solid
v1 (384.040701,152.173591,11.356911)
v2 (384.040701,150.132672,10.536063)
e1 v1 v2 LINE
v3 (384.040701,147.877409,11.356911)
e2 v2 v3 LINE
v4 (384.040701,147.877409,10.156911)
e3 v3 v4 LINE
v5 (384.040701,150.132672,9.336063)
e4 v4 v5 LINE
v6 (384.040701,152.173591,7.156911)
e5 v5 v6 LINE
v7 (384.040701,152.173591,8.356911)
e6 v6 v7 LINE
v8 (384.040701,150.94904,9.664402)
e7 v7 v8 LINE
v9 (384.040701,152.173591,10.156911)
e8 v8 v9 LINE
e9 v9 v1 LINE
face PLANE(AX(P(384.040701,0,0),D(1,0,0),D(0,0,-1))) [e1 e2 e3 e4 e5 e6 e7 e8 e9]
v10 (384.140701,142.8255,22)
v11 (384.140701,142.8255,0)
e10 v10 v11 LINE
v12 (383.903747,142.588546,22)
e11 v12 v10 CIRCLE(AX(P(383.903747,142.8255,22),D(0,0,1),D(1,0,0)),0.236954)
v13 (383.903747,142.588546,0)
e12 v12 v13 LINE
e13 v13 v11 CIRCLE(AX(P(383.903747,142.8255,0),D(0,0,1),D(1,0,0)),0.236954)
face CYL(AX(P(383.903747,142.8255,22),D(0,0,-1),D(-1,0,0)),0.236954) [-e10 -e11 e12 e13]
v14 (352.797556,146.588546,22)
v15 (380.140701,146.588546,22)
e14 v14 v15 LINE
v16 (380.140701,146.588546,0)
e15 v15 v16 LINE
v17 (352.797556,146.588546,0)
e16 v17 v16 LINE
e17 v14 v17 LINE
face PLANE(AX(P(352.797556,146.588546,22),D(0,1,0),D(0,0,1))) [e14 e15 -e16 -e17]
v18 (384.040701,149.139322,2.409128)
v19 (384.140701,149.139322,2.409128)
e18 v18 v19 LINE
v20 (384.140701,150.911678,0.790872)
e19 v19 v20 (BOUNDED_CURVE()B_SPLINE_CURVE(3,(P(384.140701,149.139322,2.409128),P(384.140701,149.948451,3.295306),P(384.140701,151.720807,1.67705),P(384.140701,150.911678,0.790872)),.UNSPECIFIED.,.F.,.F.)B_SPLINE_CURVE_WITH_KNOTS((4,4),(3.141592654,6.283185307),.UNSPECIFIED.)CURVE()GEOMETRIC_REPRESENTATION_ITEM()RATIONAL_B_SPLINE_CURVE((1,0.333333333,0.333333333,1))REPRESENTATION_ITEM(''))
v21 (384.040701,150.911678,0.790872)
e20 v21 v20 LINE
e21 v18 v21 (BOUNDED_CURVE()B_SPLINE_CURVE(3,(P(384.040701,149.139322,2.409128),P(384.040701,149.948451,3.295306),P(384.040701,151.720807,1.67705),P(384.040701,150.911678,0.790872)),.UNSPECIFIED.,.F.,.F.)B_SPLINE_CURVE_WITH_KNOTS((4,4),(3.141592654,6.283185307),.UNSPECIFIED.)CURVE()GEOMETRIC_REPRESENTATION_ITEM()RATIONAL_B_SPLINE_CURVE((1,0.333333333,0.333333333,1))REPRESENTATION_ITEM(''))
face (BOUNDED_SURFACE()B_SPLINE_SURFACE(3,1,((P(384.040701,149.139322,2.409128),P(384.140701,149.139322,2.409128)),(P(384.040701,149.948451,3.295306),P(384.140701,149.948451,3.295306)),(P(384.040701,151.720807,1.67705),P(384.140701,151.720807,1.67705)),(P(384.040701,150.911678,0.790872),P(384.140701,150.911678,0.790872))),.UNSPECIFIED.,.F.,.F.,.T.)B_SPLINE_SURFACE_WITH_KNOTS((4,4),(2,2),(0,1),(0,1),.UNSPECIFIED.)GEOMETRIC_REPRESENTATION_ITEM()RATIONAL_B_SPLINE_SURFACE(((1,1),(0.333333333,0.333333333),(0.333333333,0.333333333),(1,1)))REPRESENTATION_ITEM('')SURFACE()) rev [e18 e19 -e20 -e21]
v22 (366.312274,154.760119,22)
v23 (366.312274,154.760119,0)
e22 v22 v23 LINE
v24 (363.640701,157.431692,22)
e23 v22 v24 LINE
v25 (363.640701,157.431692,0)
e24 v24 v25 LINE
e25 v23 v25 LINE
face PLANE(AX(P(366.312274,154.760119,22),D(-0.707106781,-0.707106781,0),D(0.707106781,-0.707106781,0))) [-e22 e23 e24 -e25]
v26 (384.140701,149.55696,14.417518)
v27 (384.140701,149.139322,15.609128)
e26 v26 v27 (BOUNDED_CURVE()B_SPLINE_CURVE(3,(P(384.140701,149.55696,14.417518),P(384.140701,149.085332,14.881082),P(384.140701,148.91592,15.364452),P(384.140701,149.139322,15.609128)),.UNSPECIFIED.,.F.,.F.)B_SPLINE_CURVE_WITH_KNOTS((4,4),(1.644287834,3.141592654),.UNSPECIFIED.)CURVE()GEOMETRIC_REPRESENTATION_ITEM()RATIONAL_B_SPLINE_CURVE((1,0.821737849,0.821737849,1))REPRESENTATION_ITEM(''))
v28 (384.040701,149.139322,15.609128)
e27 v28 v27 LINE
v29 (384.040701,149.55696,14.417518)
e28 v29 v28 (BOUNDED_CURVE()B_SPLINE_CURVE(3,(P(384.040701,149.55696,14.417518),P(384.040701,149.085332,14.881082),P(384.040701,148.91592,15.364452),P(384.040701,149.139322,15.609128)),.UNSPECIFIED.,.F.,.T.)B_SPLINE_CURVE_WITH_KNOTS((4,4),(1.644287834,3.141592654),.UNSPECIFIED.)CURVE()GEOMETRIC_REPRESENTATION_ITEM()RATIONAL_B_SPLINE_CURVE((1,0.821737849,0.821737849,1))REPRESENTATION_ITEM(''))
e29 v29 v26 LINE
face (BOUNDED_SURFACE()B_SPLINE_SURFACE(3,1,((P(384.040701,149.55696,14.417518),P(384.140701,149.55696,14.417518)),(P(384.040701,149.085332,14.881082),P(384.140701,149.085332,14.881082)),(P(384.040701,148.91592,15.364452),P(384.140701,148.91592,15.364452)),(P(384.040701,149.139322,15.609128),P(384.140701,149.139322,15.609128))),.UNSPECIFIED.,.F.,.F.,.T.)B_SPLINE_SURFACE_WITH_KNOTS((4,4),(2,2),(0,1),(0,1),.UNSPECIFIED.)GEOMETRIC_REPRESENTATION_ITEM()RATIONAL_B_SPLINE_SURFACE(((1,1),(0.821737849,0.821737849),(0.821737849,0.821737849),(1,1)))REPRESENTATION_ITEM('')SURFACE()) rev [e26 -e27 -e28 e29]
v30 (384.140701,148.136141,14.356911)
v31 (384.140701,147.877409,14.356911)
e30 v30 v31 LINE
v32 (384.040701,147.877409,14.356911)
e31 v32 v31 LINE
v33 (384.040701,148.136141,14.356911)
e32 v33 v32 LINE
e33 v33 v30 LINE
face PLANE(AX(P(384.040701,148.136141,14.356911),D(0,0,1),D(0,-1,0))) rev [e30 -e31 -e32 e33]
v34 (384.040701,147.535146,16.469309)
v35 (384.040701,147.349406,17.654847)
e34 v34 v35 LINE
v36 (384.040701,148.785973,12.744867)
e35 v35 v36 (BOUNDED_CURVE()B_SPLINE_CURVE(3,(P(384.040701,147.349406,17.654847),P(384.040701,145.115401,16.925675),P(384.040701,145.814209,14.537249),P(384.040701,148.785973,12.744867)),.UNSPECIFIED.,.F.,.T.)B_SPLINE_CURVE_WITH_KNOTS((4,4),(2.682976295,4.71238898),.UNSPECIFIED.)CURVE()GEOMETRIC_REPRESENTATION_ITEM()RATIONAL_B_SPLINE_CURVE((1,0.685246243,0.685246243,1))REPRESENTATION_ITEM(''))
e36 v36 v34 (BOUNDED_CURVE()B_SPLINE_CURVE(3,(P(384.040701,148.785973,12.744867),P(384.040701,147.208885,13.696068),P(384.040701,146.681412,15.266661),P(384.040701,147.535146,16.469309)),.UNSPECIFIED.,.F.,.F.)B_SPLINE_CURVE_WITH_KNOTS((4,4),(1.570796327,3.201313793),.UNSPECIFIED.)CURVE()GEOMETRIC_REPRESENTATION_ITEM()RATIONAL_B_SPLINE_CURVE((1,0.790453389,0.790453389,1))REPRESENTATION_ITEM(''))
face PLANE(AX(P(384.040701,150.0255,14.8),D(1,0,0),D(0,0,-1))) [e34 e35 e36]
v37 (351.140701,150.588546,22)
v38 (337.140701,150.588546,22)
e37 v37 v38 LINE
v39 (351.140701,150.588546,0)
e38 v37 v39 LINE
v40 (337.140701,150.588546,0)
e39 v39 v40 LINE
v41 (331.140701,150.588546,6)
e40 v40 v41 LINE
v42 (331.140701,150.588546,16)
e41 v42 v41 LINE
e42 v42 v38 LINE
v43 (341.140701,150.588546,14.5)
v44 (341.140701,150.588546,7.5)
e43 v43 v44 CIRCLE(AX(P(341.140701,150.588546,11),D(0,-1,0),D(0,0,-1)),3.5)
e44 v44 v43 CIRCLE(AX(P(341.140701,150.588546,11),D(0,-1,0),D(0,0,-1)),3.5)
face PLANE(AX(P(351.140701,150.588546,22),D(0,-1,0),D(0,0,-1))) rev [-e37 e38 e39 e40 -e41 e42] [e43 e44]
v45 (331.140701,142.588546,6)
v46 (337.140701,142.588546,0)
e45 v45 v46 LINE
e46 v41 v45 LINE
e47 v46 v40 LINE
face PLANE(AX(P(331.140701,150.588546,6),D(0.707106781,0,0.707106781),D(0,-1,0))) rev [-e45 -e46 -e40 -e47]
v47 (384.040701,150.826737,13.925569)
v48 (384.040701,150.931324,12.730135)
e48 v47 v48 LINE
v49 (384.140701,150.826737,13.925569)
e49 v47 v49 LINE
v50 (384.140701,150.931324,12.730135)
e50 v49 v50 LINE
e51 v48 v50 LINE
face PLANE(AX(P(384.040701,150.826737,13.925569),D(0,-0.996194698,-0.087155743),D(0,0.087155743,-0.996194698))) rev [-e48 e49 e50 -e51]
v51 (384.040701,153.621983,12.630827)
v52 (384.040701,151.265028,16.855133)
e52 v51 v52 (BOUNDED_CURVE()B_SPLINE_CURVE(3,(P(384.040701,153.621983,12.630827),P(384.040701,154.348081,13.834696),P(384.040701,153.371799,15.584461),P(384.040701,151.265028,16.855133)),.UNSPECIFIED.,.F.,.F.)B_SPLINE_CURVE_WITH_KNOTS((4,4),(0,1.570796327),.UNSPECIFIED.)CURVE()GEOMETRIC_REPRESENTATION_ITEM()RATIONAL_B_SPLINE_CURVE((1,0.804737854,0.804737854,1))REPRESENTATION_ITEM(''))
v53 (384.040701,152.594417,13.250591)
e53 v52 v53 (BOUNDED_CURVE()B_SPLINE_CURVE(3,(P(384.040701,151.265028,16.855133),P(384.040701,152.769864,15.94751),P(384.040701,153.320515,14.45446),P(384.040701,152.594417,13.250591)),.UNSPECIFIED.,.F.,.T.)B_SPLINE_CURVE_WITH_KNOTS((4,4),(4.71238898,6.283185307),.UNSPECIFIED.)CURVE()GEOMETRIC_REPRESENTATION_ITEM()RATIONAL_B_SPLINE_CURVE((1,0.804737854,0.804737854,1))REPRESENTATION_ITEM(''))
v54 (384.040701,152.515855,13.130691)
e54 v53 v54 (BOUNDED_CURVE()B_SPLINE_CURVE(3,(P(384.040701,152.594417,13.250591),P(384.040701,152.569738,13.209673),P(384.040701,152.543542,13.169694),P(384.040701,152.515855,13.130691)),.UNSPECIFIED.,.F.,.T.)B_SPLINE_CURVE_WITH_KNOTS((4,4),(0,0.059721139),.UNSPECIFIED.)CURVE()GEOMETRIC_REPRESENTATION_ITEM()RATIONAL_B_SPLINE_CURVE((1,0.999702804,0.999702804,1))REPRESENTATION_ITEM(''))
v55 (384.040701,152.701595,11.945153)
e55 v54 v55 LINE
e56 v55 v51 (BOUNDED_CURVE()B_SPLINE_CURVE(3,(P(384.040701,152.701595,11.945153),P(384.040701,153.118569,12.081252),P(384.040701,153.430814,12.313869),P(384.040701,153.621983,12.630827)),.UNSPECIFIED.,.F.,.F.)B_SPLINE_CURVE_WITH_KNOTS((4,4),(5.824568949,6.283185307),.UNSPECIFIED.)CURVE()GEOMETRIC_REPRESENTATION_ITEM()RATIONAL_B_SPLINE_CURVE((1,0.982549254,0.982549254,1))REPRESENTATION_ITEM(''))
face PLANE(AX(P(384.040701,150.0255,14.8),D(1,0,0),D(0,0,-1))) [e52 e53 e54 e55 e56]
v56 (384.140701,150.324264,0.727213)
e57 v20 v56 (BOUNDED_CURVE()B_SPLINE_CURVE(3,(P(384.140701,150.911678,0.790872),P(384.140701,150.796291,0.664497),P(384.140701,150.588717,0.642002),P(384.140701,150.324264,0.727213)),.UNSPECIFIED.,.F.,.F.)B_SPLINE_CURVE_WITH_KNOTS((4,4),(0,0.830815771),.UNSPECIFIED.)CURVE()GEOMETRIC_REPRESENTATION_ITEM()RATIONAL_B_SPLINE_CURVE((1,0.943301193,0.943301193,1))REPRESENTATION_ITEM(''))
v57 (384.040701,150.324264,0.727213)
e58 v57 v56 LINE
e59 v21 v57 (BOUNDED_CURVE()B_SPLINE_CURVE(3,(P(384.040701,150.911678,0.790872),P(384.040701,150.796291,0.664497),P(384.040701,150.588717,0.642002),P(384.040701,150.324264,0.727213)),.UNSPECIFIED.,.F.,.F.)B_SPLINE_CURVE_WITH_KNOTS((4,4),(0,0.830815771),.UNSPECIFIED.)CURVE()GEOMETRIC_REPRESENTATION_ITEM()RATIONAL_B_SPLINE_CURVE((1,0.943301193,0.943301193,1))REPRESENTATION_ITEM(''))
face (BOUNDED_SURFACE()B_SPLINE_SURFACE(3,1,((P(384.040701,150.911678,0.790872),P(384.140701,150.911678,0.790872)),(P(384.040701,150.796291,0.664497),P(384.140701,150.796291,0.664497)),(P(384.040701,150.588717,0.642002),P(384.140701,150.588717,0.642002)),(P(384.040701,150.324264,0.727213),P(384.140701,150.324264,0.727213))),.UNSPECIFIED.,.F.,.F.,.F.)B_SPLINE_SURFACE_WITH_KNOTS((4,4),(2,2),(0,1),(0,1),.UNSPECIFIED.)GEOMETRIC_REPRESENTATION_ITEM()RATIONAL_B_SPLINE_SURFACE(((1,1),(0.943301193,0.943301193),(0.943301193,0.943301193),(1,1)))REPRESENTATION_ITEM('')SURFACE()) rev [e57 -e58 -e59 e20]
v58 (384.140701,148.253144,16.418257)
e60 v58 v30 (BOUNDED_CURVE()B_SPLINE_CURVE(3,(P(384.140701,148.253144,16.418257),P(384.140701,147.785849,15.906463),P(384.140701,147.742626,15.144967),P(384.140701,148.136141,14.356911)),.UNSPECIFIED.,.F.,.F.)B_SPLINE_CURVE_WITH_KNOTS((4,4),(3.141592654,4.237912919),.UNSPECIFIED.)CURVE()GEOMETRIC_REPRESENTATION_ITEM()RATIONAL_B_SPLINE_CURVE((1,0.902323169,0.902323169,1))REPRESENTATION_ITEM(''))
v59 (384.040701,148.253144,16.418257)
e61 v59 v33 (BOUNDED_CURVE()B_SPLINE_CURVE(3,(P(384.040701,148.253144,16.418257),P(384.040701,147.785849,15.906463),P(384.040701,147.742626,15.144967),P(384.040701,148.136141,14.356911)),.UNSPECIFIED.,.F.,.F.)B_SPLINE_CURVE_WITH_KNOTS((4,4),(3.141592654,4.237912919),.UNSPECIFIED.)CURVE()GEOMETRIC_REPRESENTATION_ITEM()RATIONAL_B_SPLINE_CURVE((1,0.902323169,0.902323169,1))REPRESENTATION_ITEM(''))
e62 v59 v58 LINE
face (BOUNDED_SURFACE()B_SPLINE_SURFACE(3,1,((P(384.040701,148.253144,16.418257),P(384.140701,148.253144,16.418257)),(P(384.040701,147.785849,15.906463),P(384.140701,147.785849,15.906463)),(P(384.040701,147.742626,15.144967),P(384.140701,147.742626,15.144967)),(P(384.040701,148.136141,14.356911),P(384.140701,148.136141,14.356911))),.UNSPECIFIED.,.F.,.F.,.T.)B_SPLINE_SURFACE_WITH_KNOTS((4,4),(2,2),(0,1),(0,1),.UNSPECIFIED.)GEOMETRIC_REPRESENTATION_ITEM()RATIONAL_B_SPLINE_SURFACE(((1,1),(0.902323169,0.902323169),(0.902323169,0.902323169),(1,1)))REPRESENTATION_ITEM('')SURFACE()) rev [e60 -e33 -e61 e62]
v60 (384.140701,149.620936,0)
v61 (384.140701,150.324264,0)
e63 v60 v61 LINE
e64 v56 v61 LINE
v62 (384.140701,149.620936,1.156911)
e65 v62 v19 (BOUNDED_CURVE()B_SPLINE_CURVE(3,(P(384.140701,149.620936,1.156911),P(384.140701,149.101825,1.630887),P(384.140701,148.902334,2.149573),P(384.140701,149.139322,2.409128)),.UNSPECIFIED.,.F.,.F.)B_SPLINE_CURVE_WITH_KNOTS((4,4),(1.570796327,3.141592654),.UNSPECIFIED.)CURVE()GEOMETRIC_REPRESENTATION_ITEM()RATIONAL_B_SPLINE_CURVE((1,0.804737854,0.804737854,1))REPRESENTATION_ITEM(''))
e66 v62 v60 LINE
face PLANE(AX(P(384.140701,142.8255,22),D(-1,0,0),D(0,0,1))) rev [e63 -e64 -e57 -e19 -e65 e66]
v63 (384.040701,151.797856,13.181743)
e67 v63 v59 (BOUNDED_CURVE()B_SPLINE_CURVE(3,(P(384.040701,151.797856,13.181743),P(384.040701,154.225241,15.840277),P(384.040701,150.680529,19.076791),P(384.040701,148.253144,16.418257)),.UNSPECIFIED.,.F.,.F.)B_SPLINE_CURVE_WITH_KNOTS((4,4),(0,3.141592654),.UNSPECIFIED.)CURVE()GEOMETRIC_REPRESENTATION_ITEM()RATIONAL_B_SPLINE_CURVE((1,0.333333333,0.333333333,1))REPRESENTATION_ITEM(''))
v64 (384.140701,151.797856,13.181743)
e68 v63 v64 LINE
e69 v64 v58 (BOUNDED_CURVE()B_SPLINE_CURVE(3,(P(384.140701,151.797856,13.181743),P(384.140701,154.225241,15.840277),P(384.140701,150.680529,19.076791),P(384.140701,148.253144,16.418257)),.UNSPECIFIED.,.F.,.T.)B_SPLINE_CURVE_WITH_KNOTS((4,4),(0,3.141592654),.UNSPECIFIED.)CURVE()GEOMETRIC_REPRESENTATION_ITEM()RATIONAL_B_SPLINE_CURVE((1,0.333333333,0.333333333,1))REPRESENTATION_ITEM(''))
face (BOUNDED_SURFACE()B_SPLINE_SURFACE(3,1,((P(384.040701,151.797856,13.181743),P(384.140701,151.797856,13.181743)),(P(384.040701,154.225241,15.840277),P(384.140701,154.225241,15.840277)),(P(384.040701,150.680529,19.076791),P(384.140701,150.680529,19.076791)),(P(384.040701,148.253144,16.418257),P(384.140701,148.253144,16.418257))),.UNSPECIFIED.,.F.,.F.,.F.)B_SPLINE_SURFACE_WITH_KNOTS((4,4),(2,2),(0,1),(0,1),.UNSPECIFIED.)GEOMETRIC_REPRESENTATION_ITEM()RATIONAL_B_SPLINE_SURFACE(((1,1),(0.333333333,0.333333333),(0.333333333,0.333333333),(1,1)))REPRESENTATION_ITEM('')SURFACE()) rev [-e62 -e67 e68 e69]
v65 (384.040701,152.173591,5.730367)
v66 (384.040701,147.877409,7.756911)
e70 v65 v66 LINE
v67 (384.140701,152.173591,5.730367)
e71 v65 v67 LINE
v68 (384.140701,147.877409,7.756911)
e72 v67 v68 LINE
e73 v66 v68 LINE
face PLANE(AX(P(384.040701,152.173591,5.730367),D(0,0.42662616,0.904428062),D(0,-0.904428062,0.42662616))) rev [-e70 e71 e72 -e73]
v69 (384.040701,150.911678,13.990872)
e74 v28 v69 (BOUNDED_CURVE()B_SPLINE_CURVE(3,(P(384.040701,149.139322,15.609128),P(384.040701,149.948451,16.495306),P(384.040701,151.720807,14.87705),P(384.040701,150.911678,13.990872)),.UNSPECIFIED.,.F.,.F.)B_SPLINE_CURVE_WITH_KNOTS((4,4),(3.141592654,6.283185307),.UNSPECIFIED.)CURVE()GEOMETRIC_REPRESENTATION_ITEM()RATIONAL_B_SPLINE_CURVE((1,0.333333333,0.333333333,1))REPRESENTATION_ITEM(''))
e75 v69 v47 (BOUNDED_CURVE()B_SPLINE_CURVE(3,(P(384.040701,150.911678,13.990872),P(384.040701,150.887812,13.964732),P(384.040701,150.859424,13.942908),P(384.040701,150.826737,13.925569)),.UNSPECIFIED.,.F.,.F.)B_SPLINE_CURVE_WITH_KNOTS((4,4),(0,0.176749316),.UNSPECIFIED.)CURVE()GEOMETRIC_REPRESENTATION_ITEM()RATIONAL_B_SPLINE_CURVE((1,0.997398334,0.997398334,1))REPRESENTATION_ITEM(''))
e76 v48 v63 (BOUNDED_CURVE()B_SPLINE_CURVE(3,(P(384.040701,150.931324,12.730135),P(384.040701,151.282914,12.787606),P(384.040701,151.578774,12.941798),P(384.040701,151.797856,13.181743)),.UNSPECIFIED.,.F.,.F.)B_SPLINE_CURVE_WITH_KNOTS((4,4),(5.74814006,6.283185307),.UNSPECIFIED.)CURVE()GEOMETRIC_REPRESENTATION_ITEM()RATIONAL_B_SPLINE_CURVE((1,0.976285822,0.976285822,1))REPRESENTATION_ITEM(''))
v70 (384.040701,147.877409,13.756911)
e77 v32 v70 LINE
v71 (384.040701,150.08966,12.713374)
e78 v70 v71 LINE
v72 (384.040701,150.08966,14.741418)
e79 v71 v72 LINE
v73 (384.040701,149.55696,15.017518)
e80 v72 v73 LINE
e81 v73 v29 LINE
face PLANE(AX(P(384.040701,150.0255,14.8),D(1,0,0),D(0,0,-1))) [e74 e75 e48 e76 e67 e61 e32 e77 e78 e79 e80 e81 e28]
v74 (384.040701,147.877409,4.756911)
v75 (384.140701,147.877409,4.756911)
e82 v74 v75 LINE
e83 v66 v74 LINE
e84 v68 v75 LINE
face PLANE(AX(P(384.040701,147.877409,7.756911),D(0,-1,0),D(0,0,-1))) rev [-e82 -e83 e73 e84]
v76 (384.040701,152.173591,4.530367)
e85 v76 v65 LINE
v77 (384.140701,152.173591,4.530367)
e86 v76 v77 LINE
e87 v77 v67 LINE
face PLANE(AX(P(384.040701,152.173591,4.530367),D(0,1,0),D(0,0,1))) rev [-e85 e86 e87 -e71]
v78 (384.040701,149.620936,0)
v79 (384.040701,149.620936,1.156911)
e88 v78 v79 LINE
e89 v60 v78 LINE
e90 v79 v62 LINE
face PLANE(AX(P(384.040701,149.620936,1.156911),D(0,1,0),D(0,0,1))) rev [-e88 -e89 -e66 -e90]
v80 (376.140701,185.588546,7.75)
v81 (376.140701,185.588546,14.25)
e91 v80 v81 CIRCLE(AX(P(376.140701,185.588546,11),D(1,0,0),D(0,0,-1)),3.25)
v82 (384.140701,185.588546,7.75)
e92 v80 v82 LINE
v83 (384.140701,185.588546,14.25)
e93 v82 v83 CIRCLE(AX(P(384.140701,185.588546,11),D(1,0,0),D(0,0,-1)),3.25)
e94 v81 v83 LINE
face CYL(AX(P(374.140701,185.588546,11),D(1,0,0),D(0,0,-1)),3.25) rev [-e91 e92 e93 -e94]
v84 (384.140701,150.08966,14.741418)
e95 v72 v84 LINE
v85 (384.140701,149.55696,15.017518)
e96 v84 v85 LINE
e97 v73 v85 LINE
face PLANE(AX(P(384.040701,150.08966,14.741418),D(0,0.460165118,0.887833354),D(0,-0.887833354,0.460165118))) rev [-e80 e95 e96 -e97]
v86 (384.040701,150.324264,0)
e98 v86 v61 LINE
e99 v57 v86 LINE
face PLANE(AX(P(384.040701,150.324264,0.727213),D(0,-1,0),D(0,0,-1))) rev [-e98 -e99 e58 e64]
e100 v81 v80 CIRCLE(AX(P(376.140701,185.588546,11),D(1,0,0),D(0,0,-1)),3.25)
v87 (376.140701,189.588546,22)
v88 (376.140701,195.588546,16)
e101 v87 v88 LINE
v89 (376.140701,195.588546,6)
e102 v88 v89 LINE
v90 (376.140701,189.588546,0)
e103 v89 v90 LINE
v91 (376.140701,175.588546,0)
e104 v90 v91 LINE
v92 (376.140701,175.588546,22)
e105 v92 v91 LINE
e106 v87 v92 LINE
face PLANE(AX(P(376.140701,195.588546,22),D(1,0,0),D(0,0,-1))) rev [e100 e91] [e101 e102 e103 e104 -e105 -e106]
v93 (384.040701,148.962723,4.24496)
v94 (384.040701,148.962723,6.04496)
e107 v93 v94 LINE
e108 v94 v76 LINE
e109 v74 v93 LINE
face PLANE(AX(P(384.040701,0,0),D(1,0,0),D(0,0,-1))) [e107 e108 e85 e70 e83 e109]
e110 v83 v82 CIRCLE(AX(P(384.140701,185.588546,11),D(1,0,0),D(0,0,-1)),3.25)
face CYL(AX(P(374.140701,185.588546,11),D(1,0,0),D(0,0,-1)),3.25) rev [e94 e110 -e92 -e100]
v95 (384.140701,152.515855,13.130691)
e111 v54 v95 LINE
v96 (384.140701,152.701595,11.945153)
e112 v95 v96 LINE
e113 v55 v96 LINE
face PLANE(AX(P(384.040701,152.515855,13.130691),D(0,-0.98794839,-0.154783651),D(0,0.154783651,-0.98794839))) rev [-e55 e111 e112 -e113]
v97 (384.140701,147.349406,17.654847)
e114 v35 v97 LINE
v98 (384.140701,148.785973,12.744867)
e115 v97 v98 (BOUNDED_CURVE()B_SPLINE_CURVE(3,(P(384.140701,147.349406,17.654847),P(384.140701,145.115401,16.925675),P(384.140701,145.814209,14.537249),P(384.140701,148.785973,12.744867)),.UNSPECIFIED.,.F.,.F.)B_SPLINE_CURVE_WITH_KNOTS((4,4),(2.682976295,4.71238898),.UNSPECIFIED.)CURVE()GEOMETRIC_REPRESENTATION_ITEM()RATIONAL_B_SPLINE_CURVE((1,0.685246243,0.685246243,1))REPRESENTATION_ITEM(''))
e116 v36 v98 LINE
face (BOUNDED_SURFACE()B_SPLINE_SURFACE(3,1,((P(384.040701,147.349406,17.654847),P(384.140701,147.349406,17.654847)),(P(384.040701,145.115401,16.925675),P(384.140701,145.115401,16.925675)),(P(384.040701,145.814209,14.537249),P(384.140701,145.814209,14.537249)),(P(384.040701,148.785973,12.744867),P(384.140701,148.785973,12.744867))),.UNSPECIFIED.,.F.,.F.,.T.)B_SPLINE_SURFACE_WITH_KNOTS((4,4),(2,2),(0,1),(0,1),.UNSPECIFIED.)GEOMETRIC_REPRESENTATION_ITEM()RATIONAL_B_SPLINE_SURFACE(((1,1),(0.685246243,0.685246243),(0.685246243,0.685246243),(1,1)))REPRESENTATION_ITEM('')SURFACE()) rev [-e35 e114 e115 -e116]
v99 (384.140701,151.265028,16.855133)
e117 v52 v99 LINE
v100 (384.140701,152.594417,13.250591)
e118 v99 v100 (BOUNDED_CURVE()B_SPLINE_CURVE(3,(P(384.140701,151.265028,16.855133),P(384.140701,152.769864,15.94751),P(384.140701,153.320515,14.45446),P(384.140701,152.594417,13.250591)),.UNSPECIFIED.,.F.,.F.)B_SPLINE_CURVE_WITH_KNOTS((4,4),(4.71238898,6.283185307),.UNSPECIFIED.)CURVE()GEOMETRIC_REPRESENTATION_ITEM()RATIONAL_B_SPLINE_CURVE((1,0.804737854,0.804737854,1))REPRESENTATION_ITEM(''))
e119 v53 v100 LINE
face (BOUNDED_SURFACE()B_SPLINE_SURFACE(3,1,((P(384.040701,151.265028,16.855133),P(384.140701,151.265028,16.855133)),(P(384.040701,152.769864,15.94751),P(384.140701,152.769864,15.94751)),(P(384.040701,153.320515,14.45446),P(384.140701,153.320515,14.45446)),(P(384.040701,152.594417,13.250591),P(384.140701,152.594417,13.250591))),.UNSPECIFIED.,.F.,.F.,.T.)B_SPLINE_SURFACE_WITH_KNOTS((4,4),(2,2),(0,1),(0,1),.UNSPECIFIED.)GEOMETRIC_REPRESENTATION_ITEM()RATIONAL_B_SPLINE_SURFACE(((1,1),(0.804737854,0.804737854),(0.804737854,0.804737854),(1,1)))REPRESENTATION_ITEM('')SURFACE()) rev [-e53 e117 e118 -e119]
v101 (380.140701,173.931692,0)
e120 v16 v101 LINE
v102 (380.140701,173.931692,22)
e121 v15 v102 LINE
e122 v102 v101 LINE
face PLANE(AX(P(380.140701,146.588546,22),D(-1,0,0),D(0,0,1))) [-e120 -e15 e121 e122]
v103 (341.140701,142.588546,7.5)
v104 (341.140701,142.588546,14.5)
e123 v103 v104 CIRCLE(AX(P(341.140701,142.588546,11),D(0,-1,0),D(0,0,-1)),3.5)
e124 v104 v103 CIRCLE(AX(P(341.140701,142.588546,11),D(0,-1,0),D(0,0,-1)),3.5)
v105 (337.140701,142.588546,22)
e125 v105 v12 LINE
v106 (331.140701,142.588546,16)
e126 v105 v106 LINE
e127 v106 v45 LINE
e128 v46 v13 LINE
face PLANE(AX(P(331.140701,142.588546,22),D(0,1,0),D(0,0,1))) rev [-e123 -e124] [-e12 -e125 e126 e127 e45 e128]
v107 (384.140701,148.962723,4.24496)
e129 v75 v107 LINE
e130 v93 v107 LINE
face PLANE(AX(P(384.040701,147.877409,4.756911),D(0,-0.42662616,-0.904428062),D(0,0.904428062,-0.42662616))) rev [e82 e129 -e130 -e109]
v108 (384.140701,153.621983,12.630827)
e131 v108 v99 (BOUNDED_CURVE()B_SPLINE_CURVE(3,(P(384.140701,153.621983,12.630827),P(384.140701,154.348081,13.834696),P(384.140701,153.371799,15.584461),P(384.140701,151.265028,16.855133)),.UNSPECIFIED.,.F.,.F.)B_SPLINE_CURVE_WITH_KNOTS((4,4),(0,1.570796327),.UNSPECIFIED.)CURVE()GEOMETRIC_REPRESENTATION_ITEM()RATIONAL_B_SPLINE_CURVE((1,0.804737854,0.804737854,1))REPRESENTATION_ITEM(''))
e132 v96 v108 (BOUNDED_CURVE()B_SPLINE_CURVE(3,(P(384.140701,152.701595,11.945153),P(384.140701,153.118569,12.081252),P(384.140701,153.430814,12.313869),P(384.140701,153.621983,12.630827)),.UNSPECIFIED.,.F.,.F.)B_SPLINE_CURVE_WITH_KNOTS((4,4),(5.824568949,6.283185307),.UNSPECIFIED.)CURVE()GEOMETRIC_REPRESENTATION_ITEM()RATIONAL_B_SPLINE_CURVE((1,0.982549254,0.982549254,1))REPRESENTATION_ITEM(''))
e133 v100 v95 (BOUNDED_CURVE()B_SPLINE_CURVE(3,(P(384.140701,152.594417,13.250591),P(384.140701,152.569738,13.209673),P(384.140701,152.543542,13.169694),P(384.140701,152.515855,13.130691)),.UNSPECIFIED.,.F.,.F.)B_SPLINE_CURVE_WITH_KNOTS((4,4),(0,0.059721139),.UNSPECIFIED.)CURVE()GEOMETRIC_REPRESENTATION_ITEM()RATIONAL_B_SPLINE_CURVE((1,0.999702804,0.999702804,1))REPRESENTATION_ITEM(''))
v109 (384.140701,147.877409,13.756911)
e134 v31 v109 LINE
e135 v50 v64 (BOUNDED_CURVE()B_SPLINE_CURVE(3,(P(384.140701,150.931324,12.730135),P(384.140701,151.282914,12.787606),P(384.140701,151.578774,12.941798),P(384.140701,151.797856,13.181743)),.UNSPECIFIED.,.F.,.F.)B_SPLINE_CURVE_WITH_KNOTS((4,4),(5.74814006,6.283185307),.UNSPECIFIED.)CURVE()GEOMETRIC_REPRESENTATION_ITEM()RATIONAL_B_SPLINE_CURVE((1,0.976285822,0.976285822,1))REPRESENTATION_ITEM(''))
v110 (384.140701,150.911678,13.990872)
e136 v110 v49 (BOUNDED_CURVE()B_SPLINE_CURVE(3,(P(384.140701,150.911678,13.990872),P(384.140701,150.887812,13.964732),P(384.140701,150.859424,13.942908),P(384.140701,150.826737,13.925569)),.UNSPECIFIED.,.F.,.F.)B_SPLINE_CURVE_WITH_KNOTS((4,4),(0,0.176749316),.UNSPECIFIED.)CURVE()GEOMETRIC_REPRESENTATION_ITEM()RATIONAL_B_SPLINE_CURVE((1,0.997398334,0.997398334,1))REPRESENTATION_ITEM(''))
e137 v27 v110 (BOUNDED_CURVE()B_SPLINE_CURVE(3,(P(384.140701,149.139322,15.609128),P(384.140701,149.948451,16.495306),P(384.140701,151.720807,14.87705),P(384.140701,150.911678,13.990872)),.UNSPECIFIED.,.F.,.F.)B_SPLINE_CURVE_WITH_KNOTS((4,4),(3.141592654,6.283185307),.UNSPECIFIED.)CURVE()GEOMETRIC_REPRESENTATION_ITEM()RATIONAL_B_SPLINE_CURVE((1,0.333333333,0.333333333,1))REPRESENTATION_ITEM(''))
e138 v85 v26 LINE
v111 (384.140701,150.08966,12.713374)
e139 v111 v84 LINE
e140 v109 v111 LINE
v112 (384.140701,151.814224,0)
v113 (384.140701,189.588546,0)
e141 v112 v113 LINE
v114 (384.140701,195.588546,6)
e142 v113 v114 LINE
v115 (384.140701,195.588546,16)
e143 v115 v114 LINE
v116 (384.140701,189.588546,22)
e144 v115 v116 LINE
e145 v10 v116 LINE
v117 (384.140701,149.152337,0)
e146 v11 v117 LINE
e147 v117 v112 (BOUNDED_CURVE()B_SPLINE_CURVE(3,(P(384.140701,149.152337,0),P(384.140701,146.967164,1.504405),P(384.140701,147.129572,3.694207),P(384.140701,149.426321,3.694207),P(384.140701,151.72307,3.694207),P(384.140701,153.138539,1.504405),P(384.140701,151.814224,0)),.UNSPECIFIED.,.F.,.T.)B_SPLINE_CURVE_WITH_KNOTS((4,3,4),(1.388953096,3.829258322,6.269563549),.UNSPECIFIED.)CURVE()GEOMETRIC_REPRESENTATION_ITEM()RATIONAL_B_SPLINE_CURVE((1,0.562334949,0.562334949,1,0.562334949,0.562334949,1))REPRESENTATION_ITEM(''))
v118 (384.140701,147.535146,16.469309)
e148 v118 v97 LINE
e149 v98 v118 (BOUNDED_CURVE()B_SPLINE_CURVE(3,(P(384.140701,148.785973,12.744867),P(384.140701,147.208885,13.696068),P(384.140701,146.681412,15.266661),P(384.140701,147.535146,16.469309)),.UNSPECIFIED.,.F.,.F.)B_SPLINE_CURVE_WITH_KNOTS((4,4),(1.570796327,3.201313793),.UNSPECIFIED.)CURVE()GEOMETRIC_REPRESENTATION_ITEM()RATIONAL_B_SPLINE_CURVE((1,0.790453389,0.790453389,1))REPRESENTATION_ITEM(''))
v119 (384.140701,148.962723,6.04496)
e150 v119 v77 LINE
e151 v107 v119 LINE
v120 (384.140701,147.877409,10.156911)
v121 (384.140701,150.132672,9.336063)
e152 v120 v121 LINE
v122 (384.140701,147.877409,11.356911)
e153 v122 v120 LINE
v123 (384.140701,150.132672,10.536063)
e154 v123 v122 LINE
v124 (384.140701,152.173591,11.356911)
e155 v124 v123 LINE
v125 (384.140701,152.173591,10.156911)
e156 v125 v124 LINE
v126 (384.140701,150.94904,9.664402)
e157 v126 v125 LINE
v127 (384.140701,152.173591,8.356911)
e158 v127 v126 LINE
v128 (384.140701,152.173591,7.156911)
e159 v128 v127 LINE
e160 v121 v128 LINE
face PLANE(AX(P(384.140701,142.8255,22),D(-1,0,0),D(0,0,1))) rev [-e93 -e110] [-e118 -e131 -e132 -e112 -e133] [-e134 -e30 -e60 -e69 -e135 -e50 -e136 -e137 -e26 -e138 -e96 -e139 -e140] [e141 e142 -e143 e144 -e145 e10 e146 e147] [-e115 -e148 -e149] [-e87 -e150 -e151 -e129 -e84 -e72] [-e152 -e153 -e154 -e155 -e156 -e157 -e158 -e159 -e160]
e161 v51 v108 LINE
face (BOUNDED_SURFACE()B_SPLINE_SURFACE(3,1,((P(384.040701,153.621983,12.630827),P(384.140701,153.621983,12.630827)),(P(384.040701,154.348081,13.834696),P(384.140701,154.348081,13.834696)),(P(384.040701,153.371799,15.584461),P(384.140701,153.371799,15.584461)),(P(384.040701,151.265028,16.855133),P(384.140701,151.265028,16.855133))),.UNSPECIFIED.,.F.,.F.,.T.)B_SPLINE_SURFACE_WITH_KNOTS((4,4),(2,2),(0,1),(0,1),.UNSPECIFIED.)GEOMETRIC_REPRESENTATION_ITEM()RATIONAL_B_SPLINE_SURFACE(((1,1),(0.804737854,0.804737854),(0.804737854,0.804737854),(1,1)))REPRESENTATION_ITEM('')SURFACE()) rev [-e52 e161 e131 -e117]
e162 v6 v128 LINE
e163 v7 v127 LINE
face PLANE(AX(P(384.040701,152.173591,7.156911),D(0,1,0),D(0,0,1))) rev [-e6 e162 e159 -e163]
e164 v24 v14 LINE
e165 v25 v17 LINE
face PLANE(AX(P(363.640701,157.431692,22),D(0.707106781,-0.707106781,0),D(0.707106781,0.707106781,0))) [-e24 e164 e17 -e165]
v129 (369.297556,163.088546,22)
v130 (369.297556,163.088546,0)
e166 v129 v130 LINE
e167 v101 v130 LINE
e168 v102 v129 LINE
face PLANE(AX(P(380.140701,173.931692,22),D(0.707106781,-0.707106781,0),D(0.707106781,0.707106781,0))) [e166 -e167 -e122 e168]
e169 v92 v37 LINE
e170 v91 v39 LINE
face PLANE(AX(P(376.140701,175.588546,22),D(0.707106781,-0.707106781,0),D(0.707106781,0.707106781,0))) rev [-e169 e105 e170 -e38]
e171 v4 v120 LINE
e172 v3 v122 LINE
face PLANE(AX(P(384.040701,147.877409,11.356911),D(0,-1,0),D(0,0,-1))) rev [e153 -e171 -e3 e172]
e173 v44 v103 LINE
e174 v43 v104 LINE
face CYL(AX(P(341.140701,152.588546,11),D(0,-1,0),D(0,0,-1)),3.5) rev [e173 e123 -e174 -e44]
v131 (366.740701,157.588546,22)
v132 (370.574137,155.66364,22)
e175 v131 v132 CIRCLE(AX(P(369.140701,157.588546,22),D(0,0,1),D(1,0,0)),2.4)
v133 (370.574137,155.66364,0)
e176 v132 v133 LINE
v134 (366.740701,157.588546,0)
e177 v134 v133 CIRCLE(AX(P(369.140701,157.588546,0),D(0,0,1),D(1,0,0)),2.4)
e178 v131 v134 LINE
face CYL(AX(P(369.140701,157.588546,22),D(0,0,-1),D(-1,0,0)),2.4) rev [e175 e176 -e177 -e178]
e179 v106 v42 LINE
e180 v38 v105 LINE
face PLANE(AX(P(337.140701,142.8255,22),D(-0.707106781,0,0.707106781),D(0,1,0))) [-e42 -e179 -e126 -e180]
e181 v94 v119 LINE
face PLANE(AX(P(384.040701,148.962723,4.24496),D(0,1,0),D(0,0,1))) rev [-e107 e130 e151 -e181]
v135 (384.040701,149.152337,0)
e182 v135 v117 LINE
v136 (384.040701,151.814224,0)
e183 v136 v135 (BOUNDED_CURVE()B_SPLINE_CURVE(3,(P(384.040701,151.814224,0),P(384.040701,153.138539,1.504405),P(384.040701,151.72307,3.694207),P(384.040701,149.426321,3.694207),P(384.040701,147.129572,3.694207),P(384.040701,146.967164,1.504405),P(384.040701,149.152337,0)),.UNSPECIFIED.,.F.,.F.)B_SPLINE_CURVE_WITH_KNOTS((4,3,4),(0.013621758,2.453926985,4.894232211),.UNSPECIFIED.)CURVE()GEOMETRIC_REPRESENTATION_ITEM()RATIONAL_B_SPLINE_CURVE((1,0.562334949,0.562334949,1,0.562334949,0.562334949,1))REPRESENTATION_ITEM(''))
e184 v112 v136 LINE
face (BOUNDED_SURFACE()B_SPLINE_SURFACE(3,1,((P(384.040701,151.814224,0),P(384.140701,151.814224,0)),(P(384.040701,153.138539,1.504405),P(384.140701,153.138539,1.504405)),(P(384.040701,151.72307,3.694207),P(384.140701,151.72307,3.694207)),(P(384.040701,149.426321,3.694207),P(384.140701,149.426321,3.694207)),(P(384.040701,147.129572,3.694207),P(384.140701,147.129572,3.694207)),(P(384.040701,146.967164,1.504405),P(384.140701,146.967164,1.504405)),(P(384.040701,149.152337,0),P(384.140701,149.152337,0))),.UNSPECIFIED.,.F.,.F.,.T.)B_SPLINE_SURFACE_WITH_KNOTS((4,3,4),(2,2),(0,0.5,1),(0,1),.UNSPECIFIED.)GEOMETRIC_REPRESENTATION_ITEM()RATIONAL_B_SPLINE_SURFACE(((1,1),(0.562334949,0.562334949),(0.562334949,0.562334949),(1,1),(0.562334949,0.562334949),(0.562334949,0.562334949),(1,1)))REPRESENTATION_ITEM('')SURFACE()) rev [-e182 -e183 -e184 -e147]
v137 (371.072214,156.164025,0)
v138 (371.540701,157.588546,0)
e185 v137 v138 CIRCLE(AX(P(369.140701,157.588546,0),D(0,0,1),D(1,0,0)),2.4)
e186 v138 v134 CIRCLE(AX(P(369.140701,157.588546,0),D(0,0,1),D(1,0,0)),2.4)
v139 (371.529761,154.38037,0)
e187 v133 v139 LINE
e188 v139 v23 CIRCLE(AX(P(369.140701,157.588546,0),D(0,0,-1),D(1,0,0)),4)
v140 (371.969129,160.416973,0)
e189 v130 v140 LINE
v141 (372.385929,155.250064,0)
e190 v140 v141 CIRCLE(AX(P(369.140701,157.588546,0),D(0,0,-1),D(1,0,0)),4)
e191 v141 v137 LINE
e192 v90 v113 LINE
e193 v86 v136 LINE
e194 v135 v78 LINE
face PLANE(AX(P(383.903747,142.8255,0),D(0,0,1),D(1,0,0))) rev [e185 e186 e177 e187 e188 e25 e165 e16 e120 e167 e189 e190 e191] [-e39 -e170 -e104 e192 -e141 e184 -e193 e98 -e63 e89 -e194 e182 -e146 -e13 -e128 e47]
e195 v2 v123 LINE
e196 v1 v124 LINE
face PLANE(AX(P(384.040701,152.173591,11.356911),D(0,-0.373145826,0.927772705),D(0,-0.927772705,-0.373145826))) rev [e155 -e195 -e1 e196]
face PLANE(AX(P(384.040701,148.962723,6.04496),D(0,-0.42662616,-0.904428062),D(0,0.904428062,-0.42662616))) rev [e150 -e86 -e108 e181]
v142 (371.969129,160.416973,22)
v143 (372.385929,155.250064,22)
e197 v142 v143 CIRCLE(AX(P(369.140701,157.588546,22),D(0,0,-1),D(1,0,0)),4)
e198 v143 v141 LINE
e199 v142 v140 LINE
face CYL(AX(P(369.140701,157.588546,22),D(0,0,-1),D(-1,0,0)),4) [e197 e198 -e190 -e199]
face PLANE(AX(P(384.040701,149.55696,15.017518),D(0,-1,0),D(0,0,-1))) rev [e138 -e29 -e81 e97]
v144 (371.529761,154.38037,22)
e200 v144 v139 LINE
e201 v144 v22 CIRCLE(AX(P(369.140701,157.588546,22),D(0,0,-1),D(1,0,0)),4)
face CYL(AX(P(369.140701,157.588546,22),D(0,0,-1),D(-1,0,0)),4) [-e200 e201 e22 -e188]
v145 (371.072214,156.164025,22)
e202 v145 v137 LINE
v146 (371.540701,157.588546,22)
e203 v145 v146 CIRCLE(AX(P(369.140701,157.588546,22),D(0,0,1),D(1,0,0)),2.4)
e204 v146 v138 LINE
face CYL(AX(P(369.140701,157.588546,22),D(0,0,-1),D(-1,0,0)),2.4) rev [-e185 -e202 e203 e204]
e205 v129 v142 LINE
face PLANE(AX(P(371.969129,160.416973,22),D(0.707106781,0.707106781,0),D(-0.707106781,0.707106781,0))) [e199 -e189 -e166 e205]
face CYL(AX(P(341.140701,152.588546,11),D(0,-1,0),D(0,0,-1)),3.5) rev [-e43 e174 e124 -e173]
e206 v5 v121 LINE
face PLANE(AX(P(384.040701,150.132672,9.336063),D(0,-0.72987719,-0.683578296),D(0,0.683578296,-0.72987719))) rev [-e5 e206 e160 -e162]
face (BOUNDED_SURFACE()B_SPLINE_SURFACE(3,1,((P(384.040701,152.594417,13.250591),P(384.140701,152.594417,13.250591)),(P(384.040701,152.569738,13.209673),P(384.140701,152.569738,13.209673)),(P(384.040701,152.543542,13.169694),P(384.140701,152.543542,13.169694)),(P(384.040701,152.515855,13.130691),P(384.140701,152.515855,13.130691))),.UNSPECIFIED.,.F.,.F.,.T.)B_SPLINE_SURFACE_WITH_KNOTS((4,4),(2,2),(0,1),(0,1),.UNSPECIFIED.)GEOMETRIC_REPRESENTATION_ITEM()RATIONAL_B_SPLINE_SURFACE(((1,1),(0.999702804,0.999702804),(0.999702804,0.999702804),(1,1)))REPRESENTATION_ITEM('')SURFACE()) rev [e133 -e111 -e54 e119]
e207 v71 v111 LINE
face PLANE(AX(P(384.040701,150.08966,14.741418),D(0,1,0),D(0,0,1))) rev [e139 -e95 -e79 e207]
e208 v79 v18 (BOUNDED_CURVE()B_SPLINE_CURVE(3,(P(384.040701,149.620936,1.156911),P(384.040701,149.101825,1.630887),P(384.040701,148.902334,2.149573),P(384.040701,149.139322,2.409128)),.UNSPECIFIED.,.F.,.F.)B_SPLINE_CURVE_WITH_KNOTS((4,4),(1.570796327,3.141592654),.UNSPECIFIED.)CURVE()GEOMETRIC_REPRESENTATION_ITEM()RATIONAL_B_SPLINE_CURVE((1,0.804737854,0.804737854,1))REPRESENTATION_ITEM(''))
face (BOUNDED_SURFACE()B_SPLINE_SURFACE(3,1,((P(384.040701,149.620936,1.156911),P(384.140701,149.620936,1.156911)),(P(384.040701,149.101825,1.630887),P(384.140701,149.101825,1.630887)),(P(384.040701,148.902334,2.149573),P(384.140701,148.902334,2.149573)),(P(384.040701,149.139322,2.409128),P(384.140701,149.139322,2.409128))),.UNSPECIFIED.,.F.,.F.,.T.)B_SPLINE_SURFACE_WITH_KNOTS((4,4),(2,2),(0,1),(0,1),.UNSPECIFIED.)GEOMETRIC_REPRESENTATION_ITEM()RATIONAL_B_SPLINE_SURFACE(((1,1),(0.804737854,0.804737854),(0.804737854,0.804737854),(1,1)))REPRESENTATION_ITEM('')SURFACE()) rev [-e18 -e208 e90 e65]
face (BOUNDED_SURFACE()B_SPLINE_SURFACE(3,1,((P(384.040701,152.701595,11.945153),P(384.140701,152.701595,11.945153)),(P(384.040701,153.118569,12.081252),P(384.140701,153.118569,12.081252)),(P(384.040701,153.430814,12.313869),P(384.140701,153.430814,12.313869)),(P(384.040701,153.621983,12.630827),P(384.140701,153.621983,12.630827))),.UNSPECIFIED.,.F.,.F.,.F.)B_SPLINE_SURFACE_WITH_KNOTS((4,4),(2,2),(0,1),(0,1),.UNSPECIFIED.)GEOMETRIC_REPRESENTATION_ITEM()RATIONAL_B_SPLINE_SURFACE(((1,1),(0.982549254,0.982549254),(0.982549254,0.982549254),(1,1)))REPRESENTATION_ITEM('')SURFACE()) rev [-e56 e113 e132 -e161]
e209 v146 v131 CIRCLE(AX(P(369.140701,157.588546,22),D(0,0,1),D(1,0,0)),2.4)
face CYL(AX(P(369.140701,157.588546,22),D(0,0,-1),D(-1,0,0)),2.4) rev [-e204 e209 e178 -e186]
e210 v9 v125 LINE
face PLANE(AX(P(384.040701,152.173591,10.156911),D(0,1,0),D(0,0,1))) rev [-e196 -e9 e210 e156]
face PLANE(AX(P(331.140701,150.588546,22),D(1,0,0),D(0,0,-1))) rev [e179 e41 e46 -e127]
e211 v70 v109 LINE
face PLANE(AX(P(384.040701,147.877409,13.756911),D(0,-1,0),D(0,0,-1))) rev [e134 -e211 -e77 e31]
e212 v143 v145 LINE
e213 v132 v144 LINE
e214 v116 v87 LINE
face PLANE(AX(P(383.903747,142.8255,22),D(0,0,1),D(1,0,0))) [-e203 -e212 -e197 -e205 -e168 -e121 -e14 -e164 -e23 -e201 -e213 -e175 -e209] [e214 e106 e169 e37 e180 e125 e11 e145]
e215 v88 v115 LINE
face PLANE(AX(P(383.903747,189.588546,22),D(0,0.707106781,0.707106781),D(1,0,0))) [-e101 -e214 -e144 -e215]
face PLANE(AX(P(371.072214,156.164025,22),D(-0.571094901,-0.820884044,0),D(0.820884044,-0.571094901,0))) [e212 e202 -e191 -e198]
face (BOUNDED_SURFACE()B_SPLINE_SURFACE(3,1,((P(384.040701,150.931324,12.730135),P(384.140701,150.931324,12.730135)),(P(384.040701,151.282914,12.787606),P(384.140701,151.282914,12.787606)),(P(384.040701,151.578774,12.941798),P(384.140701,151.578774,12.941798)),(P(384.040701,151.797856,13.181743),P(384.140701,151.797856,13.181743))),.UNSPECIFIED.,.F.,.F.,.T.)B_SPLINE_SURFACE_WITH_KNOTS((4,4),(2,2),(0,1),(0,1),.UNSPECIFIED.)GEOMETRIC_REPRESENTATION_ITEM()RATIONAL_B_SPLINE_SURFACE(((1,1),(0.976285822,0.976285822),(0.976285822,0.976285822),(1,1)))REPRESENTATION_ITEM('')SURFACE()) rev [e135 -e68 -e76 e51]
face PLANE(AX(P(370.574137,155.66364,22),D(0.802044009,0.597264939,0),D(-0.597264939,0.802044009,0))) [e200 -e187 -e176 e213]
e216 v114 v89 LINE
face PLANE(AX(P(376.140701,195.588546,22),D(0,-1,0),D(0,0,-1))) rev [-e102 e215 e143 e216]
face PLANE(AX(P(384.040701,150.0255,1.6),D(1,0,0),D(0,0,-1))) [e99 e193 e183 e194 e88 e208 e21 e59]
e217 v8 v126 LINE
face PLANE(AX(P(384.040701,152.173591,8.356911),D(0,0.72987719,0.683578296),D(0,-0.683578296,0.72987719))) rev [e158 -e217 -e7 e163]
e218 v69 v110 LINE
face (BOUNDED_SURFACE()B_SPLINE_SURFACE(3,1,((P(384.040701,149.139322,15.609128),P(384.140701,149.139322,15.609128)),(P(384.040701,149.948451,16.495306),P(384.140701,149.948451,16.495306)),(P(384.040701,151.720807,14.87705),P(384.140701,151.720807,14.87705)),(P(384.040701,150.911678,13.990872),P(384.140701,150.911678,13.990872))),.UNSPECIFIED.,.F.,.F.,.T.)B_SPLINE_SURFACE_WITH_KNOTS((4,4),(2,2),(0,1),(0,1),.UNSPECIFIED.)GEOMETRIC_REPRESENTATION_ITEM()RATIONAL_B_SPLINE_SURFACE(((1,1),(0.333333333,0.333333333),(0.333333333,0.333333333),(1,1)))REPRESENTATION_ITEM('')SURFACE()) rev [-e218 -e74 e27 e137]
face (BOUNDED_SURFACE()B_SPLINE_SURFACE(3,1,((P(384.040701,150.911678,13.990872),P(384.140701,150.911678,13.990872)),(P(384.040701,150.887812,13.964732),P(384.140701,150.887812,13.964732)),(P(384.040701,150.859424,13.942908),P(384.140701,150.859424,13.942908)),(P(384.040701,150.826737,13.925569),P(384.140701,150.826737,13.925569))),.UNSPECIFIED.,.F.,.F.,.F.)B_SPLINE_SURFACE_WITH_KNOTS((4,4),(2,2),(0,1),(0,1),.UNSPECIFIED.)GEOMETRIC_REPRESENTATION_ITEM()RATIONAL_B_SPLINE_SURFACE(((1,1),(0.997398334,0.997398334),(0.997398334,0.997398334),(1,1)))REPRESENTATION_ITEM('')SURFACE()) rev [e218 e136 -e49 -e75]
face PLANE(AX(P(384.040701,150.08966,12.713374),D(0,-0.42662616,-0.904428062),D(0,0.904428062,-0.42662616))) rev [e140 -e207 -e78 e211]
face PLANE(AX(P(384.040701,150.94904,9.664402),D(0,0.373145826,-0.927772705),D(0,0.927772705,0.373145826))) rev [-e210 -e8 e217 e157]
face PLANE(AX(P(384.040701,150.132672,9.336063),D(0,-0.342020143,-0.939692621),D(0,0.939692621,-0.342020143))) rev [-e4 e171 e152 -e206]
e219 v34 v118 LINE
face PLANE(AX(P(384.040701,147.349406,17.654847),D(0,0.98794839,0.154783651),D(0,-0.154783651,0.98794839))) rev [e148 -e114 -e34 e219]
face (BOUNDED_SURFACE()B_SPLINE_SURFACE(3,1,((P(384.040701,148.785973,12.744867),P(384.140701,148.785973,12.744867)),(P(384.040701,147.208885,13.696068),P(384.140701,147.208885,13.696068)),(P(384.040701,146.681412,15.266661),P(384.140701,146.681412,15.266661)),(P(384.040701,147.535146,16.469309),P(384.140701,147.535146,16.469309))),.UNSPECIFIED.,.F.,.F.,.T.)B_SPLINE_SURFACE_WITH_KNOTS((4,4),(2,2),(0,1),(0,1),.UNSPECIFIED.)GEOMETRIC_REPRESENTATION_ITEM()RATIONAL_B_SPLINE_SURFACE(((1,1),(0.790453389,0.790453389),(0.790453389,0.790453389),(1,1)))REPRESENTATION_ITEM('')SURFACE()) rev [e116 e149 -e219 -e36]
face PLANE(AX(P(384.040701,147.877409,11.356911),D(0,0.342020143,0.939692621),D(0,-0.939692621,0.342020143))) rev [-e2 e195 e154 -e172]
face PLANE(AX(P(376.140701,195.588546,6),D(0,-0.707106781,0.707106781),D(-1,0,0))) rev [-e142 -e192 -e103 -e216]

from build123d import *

# Parameters (mm, degrees)
EXTRUDE_1_DEPTH     = 22
SKETCH_1_R          = 3.5
CUT_EXTRUDE_1_DEPTH = 10
SKETCH_3_R          = 3.25
CUT_EXTRUDE_2_DEPTH = 10
CUT_EXTRUDE_3_DEPTH = 0.1
CHAMFER_2_SIZE      = 6


with BuildPart() as part:
    # Model → 凸台-拉伸1 (new body)
    with BuildSketch(Plane.XY):
        with BuildLine():
            Line((376.14070145, 195.588546008), (384.14070145, 195.588546008))
            Line((384.14070145, 195.588546008), (384.14070145, 142.825500368))
            ThreePointArc((384.14070145, 142.825500368), (384.071299125, 142.657948334), (383.90374709, 142.588546008))
            Line((383.90374709, 142.588546008), (331.14070145, 142.588546008))
            Line((331.14070145, 142.588546008), (331.14070145, 150.588546008))
            Line((331.14070145, 150.588546008), (351.14070145, 150.588546008))
            Line((351.14070145, 150.588546008), (376.14070145, 175.588546008))
            Line((376.14070145, 175.588546008), (376.14070145, 195.588546008))
        make_face()
        with BuildLine():
            Line((352.797555699, 146.588546008), (380.14070145, 146.588546008))
            Line((380.14070145, 146.588546008), (380.14070145, 173.931691759))
            Line((380.14070145, 173.931691759), (369.297555699, 163.088546008))
            Line((369.297555699, 163.088546008), (371.969128574, 160.416973133))
            ThreePointArc((371.969128574, 160.416973133), (373.12775021, 157.910170293), (372.385928963, 155.25006394))
            Line((372.385928963, 155.25006394), (371.072213777, 156.164024991))
            ThreePointArc((371.072213777, 156.164024991), (367.439726654, 159.281674694), (370.574137304, 155.663640387))
            Line((370.574137304, 155.663640387), (371.529761206, 154.380369972))
            ThreePointArc((371.529761206, 154.380369972), (368.850334045, 153.599099083), (366.312274325, 154.760118884))
            Line((366.312274325, 154.760118884), (363.64070145, 157.431691759))
            Line((363.64070145, 157.431691759), (352.797555699, 146.588546008))
        make_face(mode=Mode.SUBTRACT)
    extrude(amount=EXTRUDE_1_DEPTH)

    # 草图1 → 切除-拉伸1 (cut)
    with BuildSketch(Plane(origin=(0, 142.588546008, 0), x_dir=(-1, 0, 0), z_dir=(0, -1, 0))):
        with Locations(Location((-341.14070145, -11, 0), (0, 0, 90))):
            Circle(SKETCH_1_R)
        with Locations((-341.14070145, -41)):
            Circle(SKETCH_1_R)
    extrude(amount=-CUT_EXTRUDE_1_DEPTH, mode=Mode.SUBTRACT)

    # 草图3 → 切除-拉伸2 (cut)
    with BuildSketch(Plane(origin=(384.14070145, 0, 0), x_dir=(0, 0, -1), z_dir=(1, 0, 0))):
        with Locations((-11, 185.588546008)):
            Circle(SKETCH_3_R)
        with Locations((19, 185.588546008)):
            Circle(SKETCH_3_R)
    extrude(amount=-CUT_EXTRUDE_2_DEPTH, mode=Mode.SUBTRACT)

    # 草图4 → 切除-拉伸3 (cut)
    with BuildSketch(Plane(origin=(384.14070145, 0, 0), x_dir=(0, 0, -1), z_dir=(1, 0, 0))):
        with BuildLine():
            Line((-1.156910998, 149.620936237), (0.265081975, 149.620936237))
            add(Edge.make_bspline(
                [(0.472786894, 150.324263564), (0.930359486, 153.582209756), (-2.160166716, 151.852897671), (-5.250692919, 150.123585587), (-3.22217607, 148.256737296), (-1.193659222, 146.389889004), (0.265081975, 149.620936237)],
                knots=[2.310776883, 2.310776883, 2.310776883, 4.295504112, 4.295504112, 6.280231341, 6.280231341, 8.26495857, 8.26495857, 8.26495857], degree=2, weights=[1, 0.546712287, 1, 0.546712287, 1, 0.546712287, 1]))
            Line((0.472786894, 150.324263564), (-0.727213106, 150.324263564))
            add(Edge.make_bspline(
                [(-0.727213106, 150.324263564), (-0.331693937, 151.551759326), (-1.551251149, 150.835698352), (-2.770808361, 150.119637377), (-2.499443953, 149.28370119), (-2.228079545, 148.447765002), (-1.156910998, 149.620936237)],
                knots=[2.310776883, 2.310776883, 2.310776883, 4.1585118, 4.1585118, 6.006246717, 6.006246717, 7.853981634, 7.853981634, 7.853981634], degree=2, weights=[1, 0.602738677, 1, 0.602738677, 1, 0.602738677, 1]))
        make_face()
        with BuildLine():
            Line((-13.925569034, 150.826737427), (-12.730135397, 150.931324318))
            add(Edge.make_bspline(
                [(-12.730135397, 150.931324318), (-13.532943041, 155.84269164), (-16.525470552, 150.700825597), (-19.517998063, 145.558959554), (-14.356910998, 148.136141251)],
                knots=[2.606547406, 2.606547406, 2.606547406, 4.993026489, 4.993026489, 7.379505572, 7.379505572, 7.379505572], degree=2, weights=[1, 0.368650437, 1, 0.368650437, 1]))
            Line((-14.356910998, 148.136141251), (-14.356910998, 147.877409345))
            Line((-14.356910998, 147.877409345), (-13.756910998, 147.877409345))
            Line((-13.756910998, 147.877409345), (-12.713374, 150.089660335))
            Line((-12.713374, 150.089660335), (-14.741418493, 150.089660335))
            Line((-14.741418493, 150.089660335), (-15.017517564, 149.556960323))
            Line((-15.017517564, 149.556960323), (-14.417517564, 149.556960323))
            add(Edge.make_bspline(
                [(-13.925569034, 150.826737427), (-14.690411989, 152.268585428), (-15.646229095, 149.801508889), (-16.602046201, 147.334432349), (-14.417517564, 149.556960323)],
                knots=[2.964843337, 2.964843337, 2.964843337, 5.372666732, 5.372666732, 7.780490127, 7.780490127, 7.780490127], degree=2, weights=[1, 0.358709137, 1, 0.358709137, 1]))
        make_face()
        Polygon((-11.356910998, 147.877409345), (-10.156910998, 147.877409345), (-9.336062654, 150.132671635), (-7.156910998, 152.173591391), (-8.356910998, 152.173591391), (-9.664401992, 150.949039538), (-10.156910998, 152.173591391), (-11.356910998, 152.173591391), (-10.536062654, 150.132671635), align=None)
        Polygon((-5.73036657, 152.173591391), (-7.756910998, 147.877409345), (-4.756910998, 147.877409345), (-4.244959606, 148.96272302), (-6.044959606, 148.96272302), (-4.53036657, 152.173591391), align=None)
        with BuildLine():
            Line((-13.130690832, 152.515854721), (-11.945152764, 152.701595103))
            add(Edge.make_bspline(
                [(-11.945152764, 152.701595103), (-13.36499983, 157.051657906), (-16.85513293, 151.265027956)],
                knots=[2.682976295, 2.682976295, 2.682976295, 4.71238898, 4.71238898, 4.71238898], degree=2, weights=[1, 0.527869365, 1]))
            add(Edge.make_bspline(
                [(-13.130690832, 152.515854721), (-15.210313594, 153.992133359), (-16.85513293, 151.265027956)],
                knots=[3.081871514, 3.081871514, 3.081871514, 4.71238898, 4.71238898, 4.71238898], degree=2, weights=[1, 0.685680084, 1]))
        make_face()
        with BuildLine():
            Line((-17.654847236, 147.349405634), (-16.469309168, 147.535146015))
            add(Edge.make_bspline(
                [(-16.469309168, 147.535146015), (-14.389686406, 146.058867378), (-12.74486707, 148.78597278)],
                knots=[6.223464168, 6.223464168, 6.223464168, 7.853981634, 7.853981634, 7.853981634], degree=2, weights=[1, 0.685680084, 1]))
            add(Edge.make_bspline(
                [(-17.654847236, 147.349405634), (-16.23500017, 142.999342831), (-12.74486707, 148.78597278)],
                knots=[5.824568949, 5.824568949, 5.824568949, 7.853981634, 7.853981634, 7.853981634], degree=2, weights=[1, 0.527869365, 1]))
        make_face()
    extrude(amount=-CUT_EXTRUDE_3_DEPTH, mode=Mode.SUBTRACT)

    # 倒角2
    chamfer_2_edges = [part.edges().sort_by_distance(p)[0] for p in [
        (331.14070145, 146.588546008, 22),
        (380.14070145, 195.588546008, 22),
        (380.14070145, 195.588546008, 0),
        (331.14070145, 146.588546008, 0),
    ]]
    chamfer(chamfer_2_edges, length=CHAMFER_2_SIZE)


solid = part.part
